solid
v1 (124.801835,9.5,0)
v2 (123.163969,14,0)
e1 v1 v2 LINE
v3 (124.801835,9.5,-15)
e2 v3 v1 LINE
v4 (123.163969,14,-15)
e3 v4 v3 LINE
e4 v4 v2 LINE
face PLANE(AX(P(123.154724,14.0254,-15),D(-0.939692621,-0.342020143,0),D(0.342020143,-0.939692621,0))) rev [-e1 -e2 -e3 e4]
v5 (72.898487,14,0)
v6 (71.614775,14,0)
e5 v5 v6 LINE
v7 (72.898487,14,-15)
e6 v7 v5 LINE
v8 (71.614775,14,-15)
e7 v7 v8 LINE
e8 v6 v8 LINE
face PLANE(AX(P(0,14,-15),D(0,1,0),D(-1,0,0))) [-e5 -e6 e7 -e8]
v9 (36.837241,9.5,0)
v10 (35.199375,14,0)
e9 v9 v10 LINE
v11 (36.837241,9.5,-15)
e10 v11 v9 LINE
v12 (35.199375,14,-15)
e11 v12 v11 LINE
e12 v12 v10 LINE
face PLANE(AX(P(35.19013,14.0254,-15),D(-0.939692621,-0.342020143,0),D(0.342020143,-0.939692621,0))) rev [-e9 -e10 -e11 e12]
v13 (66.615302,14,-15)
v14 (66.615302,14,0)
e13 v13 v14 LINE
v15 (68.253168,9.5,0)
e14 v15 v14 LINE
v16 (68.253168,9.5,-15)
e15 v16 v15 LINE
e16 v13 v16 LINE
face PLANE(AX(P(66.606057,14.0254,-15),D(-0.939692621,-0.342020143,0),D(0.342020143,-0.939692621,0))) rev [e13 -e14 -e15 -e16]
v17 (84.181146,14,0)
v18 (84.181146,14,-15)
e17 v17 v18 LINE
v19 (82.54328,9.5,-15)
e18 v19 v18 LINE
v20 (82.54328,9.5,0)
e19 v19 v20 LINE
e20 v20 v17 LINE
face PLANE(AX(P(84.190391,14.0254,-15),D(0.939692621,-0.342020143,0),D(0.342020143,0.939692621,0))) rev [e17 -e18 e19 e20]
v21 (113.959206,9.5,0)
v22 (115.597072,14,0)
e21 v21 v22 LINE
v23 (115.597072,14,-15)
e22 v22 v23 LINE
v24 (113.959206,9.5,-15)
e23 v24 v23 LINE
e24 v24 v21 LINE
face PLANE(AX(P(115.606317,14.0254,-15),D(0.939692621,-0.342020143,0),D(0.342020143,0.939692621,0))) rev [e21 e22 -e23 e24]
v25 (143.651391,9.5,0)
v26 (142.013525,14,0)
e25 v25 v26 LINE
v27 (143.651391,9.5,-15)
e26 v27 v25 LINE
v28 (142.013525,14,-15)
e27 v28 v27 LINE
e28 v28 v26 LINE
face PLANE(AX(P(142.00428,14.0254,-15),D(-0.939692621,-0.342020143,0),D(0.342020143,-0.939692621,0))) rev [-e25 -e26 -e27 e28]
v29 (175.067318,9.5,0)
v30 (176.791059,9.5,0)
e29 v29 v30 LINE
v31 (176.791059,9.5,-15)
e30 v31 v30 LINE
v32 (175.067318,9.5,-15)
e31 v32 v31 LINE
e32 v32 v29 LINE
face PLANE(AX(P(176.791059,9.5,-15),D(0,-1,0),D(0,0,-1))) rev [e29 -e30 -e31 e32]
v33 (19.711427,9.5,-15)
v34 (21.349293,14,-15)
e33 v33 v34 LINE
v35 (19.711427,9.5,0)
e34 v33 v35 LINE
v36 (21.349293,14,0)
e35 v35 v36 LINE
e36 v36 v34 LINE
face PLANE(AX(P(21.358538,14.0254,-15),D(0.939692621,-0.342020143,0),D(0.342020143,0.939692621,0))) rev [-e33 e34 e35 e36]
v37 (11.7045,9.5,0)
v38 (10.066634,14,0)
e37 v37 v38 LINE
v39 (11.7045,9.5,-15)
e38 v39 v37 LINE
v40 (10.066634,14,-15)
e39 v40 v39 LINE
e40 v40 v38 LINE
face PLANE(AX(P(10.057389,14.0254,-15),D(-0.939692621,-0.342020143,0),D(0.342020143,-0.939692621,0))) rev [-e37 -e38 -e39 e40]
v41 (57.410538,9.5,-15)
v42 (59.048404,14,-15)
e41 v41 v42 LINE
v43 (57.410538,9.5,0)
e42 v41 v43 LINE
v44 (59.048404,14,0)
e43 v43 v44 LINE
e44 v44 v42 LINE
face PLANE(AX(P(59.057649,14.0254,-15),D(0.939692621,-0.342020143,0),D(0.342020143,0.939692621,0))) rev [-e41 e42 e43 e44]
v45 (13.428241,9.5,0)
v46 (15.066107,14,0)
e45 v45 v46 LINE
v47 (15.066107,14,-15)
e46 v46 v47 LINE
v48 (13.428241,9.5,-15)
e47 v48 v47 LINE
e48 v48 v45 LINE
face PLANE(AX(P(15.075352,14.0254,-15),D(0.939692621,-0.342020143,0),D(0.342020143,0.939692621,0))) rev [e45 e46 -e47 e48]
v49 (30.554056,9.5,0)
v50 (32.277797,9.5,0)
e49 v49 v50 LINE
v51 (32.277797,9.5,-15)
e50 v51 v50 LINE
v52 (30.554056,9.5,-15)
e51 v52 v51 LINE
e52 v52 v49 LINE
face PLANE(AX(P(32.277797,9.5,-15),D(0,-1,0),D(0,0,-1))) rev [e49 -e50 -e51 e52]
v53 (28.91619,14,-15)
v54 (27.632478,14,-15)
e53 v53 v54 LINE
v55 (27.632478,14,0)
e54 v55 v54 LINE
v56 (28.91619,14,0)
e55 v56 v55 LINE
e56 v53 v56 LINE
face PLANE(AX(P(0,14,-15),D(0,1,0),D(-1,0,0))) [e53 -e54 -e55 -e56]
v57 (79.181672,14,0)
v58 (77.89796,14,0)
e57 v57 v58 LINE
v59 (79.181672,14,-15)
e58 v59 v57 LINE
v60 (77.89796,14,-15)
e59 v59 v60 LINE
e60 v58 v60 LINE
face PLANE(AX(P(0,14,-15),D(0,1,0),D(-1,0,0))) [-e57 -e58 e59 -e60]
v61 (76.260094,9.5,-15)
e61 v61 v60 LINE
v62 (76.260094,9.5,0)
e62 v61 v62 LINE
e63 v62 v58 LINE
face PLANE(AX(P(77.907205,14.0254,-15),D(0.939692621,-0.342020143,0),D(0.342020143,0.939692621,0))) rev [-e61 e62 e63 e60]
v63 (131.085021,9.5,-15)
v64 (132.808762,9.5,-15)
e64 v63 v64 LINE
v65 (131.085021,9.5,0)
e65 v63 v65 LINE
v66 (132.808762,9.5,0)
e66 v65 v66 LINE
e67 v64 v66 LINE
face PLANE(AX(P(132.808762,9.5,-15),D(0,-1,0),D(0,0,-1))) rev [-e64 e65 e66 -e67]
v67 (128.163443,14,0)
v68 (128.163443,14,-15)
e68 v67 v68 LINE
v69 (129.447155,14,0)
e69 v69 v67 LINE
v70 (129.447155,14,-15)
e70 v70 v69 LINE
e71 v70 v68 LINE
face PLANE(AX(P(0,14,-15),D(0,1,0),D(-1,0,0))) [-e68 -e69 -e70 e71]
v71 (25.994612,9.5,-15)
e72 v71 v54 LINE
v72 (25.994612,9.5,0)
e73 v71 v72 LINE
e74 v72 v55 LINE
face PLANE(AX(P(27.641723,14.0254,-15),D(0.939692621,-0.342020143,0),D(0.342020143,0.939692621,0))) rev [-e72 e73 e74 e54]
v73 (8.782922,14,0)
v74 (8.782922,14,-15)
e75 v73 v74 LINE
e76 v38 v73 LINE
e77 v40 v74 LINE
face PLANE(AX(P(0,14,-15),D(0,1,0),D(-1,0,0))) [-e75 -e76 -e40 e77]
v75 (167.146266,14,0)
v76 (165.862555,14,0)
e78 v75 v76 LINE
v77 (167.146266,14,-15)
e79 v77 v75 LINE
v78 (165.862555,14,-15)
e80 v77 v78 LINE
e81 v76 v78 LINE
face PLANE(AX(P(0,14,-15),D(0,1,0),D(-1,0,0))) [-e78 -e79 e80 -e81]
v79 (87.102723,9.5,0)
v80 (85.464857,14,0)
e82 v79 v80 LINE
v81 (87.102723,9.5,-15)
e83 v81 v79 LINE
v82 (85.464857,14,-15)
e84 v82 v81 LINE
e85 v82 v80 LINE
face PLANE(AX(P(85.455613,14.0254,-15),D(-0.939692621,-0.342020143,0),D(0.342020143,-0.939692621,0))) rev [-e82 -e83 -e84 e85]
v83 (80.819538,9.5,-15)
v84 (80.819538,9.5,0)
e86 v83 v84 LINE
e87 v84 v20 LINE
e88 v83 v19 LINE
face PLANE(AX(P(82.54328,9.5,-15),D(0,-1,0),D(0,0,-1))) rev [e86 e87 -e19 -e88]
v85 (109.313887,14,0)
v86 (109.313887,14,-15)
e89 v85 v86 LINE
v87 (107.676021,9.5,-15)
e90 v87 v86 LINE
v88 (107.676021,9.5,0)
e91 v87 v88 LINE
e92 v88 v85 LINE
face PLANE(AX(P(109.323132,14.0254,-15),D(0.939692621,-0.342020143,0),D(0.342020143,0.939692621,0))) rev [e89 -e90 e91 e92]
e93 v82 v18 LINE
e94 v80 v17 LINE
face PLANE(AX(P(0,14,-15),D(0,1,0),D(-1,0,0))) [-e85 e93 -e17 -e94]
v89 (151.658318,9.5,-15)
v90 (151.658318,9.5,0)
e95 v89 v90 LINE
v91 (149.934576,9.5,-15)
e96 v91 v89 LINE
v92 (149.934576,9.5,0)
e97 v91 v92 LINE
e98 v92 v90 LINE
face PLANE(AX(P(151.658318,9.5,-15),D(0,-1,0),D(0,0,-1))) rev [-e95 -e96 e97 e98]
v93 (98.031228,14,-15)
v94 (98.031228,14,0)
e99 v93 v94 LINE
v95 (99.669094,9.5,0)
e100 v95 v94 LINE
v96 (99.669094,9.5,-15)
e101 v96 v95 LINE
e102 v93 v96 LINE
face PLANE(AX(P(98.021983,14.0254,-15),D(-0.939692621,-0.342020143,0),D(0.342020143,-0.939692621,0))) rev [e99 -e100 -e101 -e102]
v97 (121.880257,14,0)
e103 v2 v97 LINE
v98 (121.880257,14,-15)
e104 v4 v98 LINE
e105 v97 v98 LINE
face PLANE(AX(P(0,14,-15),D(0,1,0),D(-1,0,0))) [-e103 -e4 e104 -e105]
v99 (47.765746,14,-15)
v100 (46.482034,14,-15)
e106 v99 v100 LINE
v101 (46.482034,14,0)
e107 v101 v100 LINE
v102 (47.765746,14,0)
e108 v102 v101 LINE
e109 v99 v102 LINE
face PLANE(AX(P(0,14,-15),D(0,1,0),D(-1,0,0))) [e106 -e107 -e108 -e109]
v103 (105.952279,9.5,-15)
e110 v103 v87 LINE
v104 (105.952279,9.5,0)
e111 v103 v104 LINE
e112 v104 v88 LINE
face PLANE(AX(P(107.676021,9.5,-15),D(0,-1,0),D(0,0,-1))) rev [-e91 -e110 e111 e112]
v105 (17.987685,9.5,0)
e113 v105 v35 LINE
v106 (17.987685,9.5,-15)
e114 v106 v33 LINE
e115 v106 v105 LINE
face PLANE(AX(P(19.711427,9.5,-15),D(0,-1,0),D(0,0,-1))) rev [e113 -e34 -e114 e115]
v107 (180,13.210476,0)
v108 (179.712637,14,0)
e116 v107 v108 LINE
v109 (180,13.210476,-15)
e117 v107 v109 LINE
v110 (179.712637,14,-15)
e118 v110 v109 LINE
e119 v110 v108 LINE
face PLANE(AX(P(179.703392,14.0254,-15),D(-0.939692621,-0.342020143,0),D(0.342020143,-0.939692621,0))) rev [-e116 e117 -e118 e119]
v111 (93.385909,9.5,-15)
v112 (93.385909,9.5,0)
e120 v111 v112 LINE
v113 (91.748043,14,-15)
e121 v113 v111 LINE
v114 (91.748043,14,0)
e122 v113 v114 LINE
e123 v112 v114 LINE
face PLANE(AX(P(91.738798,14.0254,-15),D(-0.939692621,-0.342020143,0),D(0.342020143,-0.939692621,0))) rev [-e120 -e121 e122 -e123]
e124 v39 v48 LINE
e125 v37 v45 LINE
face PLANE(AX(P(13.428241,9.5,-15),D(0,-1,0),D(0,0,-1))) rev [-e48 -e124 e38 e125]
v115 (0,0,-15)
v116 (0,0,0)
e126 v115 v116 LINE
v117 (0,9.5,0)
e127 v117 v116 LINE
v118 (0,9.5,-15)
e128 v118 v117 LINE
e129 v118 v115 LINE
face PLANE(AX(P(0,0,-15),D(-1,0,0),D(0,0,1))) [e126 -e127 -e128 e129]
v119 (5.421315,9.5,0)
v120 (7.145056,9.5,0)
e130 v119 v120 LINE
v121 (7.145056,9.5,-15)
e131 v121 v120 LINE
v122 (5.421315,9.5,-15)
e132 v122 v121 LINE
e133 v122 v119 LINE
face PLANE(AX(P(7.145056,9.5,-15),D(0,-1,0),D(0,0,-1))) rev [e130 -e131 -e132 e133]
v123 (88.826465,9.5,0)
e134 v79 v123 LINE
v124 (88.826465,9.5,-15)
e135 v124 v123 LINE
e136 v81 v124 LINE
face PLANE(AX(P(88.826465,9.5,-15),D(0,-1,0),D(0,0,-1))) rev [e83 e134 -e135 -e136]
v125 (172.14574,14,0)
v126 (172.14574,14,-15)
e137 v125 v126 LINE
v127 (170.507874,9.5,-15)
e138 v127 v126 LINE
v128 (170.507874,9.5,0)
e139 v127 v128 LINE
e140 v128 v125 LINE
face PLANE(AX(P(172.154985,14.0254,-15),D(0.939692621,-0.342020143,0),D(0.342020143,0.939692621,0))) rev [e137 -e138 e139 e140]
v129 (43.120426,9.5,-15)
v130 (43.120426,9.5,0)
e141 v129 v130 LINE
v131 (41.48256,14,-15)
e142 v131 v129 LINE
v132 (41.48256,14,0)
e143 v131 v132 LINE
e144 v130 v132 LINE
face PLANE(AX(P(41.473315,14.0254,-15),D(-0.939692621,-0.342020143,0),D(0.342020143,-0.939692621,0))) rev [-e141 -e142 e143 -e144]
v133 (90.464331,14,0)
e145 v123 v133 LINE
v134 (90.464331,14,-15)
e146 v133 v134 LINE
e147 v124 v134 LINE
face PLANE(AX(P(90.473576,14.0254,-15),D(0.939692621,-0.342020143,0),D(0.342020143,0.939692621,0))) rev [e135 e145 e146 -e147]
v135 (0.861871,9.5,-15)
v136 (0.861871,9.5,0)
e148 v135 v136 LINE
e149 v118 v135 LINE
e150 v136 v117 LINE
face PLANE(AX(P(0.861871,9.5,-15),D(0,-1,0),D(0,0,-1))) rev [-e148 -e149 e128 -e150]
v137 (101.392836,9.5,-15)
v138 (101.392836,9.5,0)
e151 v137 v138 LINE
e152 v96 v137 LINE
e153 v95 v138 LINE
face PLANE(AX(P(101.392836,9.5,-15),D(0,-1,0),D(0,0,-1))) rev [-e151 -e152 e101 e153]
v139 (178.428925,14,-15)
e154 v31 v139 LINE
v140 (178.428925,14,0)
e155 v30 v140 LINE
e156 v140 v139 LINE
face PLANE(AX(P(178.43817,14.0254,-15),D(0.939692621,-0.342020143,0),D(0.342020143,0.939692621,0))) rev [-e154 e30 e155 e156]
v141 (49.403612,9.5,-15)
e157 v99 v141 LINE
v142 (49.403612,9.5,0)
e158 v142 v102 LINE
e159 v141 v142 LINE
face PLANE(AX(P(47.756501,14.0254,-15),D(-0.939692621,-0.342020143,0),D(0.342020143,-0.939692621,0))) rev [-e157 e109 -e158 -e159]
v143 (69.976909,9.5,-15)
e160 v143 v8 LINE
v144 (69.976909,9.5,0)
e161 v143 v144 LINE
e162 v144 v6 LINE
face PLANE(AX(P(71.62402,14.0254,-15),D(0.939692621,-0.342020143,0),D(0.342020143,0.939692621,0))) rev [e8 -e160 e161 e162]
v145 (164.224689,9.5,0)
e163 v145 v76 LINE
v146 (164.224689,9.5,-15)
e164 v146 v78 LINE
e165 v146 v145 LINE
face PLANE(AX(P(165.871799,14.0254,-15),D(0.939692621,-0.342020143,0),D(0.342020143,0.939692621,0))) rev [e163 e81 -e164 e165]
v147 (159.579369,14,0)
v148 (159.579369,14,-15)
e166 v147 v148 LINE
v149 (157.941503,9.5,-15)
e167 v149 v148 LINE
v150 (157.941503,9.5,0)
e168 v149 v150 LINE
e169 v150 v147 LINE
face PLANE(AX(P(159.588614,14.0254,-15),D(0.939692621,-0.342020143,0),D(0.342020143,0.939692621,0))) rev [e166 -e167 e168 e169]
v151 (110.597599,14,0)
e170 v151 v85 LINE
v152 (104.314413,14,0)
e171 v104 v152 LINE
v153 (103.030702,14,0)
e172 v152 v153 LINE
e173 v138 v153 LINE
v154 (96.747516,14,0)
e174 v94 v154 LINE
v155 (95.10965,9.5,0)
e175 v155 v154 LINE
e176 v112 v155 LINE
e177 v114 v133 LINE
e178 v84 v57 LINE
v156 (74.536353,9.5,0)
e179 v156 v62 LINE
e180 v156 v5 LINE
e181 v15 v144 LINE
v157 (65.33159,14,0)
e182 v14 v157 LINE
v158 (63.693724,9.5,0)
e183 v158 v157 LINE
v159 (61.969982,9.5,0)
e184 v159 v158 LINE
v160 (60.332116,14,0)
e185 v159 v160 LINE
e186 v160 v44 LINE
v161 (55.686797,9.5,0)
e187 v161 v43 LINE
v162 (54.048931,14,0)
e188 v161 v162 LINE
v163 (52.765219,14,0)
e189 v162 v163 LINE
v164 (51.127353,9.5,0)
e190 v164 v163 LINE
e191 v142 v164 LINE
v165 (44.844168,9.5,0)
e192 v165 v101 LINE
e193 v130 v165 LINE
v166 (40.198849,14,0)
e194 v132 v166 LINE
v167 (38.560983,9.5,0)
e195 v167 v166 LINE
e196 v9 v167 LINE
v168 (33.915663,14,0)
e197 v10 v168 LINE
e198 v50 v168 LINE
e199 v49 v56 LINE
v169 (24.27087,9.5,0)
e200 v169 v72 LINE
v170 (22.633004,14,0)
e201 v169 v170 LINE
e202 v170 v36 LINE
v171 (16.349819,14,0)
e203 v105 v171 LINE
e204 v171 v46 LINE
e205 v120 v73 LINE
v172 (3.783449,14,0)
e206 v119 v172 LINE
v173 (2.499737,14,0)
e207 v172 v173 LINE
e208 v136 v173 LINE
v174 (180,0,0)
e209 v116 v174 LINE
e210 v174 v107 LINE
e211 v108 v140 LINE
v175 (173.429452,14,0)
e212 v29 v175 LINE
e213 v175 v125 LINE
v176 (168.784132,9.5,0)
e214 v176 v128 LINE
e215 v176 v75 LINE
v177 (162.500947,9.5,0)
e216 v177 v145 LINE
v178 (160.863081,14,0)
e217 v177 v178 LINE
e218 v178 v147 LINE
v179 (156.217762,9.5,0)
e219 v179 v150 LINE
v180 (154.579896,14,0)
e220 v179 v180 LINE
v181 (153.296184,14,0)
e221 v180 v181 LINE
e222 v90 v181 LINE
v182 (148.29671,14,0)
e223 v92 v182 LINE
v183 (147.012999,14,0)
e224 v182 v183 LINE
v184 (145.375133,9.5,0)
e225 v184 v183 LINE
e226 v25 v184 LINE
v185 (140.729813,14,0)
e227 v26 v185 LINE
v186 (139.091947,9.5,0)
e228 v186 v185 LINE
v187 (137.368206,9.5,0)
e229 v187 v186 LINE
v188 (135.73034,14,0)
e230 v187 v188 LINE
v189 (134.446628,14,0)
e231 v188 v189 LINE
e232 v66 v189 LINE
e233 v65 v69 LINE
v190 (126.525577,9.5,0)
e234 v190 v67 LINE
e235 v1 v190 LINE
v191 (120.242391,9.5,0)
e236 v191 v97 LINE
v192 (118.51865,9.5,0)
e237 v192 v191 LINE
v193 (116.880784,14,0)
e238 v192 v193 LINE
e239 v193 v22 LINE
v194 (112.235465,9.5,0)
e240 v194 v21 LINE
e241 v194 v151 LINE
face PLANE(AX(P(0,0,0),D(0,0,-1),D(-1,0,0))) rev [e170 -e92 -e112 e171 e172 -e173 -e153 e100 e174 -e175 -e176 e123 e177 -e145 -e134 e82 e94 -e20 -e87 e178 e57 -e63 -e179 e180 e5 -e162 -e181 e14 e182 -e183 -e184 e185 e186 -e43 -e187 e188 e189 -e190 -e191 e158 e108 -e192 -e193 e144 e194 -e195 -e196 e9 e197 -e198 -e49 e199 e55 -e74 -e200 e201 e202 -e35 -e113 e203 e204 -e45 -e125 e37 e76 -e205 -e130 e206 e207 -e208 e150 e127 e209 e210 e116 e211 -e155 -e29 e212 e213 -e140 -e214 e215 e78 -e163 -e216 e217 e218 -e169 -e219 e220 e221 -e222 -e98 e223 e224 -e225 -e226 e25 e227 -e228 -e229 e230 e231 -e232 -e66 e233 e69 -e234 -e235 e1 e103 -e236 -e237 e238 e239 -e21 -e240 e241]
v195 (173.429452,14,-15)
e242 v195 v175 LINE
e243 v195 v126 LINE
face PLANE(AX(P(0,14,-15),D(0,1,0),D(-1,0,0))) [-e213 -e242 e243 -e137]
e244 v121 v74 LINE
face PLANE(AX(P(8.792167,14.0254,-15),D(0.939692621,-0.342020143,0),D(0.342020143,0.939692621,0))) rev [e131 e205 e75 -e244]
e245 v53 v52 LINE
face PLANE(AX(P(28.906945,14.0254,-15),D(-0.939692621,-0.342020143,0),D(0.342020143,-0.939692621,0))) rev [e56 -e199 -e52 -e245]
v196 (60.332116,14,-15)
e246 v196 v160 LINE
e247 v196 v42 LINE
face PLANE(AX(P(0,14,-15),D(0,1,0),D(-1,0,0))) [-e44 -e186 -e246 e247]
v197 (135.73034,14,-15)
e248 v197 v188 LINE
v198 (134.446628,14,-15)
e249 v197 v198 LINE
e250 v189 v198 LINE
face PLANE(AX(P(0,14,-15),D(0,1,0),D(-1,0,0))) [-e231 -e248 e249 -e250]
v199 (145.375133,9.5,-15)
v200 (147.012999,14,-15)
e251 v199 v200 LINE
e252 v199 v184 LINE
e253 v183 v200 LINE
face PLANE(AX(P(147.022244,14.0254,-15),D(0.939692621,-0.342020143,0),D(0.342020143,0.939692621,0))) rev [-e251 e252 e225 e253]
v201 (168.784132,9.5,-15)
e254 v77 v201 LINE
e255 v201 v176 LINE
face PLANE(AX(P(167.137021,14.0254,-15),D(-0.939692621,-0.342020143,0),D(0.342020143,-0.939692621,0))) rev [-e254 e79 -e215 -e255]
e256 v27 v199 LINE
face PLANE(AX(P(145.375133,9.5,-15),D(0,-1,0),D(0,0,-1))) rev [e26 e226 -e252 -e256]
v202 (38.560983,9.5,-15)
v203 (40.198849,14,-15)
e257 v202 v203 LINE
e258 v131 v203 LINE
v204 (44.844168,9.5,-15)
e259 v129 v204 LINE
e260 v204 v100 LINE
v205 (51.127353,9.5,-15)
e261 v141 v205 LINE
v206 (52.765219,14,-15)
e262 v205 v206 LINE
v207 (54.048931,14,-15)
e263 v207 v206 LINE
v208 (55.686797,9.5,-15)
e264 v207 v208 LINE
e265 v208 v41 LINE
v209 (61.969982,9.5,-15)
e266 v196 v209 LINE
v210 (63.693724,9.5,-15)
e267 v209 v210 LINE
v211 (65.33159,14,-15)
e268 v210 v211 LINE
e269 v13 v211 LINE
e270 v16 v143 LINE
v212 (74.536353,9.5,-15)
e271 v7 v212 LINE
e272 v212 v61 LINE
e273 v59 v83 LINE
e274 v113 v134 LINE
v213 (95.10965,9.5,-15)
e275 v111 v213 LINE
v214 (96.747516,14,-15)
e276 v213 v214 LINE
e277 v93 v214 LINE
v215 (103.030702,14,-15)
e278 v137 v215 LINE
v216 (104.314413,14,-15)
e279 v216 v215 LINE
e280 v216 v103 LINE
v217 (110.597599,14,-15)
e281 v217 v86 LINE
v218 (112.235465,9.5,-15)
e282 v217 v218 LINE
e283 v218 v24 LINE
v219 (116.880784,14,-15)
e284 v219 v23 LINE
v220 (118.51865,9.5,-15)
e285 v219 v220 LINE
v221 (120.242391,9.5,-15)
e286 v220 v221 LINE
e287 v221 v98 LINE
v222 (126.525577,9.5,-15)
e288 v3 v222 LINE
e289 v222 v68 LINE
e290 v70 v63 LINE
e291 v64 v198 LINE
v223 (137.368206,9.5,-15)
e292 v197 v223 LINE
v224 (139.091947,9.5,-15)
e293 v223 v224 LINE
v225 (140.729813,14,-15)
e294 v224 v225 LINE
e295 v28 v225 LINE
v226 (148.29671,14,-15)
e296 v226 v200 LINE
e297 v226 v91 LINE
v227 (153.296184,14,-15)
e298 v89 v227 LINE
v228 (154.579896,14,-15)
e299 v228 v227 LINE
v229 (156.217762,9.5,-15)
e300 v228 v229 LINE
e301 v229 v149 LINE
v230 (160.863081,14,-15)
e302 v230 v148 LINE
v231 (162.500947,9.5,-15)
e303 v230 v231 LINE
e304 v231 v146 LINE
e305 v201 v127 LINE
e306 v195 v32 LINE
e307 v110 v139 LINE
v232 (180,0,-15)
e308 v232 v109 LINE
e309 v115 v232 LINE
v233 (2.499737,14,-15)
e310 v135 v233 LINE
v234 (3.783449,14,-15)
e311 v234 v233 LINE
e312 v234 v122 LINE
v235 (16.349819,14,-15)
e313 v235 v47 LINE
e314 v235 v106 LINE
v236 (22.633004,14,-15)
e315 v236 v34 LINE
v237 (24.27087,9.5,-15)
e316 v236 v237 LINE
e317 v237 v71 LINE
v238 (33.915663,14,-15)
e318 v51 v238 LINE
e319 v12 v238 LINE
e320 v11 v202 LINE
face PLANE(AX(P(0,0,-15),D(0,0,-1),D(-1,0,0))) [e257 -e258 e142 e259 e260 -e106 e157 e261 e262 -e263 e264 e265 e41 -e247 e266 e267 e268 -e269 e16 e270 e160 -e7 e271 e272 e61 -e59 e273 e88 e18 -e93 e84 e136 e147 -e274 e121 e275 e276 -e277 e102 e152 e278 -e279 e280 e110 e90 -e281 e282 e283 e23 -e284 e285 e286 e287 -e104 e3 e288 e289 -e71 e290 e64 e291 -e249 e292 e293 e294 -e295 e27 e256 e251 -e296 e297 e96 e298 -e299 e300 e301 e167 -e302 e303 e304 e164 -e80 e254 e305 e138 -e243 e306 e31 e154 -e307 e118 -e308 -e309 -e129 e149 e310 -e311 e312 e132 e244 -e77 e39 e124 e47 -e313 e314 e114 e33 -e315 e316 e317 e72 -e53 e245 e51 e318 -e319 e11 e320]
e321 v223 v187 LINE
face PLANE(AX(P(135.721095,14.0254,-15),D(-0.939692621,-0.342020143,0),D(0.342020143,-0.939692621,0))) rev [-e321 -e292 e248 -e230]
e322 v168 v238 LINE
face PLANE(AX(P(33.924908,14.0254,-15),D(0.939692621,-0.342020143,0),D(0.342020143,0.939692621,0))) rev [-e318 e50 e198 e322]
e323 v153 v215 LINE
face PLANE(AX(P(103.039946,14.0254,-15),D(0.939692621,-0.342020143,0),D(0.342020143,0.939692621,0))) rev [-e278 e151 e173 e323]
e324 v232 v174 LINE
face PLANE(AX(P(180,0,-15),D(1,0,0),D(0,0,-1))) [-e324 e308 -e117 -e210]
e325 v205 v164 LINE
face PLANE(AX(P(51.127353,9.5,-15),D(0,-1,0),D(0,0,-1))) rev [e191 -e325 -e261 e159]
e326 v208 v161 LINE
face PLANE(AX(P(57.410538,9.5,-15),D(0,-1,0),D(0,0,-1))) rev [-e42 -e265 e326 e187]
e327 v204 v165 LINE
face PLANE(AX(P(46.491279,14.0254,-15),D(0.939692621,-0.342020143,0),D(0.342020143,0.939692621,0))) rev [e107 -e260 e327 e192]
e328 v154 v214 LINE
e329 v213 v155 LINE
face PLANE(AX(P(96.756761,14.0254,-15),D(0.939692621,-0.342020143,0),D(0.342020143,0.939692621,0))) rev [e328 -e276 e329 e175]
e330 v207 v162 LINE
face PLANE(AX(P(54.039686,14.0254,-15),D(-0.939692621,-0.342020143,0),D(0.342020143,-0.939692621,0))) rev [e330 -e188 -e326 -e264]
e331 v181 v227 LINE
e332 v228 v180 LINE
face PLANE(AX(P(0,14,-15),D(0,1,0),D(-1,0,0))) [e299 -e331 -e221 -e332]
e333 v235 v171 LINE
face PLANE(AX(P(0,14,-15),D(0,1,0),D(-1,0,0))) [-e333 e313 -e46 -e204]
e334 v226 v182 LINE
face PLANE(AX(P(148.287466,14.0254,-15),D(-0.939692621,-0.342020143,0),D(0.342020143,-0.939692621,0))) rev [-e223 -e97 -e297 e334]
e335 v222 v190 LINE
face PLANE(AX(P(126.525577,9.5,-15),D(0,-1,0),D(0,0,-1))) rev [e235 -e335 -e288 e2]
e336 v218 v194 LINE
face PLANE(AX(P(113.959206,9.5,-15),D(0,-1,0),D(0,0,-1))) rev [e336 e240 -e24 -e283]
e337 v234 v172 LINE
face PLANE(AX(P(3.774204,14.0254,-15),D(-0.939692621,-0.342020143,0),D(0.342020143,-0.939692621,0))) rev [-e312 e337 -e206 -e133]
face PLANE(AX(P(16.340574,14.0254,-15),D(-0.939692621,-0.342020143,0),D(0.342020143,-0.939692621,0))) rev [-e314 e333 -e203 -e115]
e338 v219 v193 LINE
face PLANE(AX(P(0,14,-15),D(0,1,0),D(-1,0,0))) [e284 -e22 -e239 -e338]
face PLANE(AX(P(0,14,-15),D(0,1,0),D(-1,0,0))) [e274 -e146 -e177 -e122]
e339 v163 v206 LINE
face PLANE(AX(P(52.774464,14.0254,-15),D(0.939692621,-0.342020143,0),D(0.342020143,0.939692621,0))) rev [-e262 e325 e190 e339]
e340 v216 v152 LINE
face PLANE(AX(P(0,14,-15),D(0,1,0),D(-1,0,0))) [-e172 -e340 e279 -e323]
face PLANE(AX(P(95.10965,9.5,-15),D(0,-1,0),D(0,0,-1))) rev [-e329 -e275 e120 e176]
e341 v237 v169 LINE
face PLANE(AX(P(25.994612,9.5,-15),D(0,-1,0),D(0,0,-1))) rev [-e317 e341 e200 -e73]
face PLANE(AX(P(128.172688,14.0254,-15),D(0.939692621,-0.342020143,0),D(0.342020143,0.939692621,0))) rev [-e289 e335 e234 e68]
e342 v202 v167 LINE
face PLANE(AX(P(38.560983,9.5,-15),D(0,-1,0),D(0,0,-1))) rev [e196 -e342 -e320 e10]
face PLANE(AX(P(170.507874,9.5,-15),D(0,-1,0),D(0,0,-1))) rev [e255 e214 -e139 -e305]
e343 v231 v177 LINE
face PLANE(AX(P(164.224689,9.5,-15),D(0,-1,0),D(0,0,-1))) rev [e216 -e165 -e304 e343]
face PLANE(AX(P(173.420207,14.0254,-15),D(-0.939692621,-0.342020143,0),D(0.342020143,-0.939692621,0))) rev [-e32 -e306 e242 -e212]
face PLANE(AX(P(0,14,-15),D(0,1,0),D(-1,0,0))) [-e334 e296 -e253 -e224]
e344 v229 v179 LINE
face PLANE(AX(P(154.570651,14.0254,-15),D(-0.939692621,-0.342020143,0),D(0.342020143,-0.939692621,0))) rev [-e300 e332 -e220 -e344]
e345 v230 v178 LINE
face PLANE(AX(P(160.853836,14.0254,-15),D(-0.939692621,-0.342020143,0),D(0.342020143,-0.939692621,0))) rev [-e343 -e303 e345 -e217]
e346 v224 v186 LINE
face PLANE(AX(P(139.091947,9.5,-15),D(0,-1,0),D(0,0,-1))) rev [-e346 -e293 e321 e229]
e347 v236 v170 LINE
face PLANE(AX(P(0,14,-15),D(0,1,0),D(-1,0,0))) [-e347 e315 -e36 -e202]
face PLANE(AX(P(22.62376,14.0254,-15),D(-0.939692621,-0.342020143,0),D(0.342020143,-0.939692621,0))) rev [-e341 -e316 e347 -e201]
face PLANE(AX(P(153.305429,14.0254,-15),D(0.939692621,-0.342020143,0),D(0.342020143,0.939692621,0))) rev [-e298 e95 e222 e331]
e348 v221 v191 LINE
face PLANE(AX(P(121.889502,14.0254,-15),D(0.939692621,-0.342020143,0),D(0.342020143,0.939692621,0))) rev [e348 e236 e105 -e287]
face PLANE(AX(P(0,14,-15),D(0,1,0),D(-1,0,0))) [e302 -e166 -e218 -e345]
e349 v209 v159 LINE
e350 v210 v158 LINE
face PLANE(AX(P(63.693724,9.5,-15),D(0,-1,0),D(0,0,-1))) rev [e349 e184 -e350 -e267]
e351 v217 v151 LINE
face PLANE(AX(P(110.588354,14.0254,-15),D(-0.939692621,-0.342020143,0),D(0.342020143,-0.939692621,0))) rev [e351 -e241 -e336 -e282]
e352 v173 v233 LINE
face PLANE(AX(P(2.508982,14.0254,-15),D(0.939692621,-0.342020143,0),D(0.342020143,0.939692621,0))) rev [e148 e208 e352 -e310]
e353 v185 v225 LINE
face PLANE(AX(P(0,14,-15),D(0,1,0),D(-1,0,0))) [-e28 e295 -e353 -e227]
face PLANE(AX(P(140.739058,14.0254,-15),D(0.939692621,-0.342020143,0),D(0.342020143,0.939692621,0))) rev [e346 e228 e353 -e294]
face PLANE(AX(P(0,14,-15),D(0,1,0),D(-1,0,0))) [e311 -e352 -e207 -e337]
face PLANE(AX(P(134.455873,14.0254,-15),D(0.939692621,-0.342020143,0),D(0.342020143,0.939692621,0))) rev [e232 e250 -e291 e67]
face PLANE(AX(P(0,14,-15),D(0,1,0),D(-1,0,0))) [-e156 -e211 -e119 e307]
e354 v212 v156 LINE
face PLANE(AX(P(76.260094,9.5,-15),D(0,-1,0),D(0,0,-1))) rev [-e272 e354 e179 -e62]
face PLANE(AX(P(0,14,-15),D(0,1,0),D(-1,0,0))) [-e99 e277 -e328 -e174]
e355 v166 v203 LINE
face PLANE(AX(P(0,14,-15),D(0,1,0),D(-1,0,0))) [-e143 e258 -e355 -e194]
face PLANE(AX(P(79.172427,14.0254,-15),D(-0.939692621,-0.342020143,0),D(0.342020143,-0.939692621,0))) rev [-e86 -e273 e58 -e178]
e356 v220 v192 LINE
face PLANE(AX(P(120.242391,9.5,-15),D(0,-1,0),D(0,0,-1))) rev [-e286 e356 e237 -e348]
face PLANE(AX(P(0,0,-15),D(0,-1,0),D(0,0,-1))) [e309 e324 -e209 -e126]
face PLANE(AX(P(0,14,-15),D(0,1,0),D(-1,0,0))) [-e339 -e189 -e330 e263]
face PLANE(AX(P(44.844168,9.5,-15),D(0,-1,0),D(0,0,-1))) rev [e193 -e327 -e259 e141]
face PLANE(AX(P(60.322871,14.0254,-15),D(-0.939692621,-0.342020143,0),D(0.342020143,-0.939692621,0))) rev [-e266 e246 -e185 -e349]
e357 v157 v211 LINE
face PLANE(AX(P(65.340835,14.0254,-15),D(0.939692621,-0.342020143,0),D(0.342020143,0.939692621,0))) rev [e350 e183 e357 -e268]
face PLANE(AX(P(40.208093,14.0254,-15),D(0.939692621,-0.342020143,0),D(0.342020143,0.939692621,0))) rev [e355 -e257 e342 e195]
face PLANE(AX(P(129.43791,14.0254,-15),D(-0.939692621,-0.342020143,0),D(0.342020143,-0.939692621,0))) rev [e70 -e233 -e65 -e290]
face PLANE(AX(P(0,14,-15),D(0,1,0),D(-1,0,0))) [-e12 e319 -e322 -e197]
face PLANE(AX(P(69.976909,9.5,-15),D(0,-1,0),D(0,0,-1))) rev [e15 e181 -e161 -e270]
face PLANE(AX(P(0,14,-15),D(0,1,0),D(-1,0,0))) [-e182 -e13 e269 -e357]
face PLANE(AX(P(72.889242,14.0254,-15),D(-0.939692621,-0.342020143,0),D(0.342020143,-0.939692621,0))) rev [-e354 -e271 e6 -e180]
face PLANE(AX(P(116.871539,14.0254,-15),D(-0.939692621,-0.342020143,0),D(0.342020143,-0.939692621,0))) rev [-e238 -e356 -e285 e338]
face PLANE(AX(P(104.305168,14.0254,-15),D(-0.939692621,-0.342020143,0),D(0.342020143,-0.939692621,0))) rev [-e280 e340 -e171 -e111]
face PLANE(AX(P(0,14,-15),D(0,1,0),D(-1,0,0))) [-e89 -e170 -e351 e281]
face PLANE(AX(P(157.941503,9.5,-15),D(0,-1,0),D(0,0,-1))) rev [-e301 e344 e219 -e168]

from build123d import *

# Parameters (mm, degrees)
BLANKSKE_W        = 180
BLANKSKE_H        = 14
BLANK_DEPTH       = 15
TOOTHCUTSIM_DEPTH = 182.165670037
TEETHCUTS_COUNT   = 30
TEETHCUTS_PITCH   = 6.2831853


with BuildPart() as part:
    # BlankSke → Blank (new body)
    with BuildSketch(Plane.XY):
        with Locations((90, 7)):
            Rectangle(BLANKSKE_W, BLANKSKE_H)
    extrude(amount=-BLANK_DEPTH)

    # TooCutSkeSim → ToothCutSim (cut, through all)
    with BuildSketch(Plane.XY):
        Polygon((0.861870739, 9.5), (-0.861870739, 9.5), (-2.508981637, 14.0254), (2.508981637, 14.0254), align=None)
    toothcutsim = extrude(amount=-TOOTHCUTSIM_DEPTH, mode=Mode.SUBTRACT)

    # TeethCuts: ToothCutSim ×30
    with Locations(*[(i * TEETHCUTS_PITCH, 0, 0) for i in range(1, TEETHCUTS_COUNT)]):
        add(toothcutsim, mode=Mode.SUBTRACT)


solid = part.part
